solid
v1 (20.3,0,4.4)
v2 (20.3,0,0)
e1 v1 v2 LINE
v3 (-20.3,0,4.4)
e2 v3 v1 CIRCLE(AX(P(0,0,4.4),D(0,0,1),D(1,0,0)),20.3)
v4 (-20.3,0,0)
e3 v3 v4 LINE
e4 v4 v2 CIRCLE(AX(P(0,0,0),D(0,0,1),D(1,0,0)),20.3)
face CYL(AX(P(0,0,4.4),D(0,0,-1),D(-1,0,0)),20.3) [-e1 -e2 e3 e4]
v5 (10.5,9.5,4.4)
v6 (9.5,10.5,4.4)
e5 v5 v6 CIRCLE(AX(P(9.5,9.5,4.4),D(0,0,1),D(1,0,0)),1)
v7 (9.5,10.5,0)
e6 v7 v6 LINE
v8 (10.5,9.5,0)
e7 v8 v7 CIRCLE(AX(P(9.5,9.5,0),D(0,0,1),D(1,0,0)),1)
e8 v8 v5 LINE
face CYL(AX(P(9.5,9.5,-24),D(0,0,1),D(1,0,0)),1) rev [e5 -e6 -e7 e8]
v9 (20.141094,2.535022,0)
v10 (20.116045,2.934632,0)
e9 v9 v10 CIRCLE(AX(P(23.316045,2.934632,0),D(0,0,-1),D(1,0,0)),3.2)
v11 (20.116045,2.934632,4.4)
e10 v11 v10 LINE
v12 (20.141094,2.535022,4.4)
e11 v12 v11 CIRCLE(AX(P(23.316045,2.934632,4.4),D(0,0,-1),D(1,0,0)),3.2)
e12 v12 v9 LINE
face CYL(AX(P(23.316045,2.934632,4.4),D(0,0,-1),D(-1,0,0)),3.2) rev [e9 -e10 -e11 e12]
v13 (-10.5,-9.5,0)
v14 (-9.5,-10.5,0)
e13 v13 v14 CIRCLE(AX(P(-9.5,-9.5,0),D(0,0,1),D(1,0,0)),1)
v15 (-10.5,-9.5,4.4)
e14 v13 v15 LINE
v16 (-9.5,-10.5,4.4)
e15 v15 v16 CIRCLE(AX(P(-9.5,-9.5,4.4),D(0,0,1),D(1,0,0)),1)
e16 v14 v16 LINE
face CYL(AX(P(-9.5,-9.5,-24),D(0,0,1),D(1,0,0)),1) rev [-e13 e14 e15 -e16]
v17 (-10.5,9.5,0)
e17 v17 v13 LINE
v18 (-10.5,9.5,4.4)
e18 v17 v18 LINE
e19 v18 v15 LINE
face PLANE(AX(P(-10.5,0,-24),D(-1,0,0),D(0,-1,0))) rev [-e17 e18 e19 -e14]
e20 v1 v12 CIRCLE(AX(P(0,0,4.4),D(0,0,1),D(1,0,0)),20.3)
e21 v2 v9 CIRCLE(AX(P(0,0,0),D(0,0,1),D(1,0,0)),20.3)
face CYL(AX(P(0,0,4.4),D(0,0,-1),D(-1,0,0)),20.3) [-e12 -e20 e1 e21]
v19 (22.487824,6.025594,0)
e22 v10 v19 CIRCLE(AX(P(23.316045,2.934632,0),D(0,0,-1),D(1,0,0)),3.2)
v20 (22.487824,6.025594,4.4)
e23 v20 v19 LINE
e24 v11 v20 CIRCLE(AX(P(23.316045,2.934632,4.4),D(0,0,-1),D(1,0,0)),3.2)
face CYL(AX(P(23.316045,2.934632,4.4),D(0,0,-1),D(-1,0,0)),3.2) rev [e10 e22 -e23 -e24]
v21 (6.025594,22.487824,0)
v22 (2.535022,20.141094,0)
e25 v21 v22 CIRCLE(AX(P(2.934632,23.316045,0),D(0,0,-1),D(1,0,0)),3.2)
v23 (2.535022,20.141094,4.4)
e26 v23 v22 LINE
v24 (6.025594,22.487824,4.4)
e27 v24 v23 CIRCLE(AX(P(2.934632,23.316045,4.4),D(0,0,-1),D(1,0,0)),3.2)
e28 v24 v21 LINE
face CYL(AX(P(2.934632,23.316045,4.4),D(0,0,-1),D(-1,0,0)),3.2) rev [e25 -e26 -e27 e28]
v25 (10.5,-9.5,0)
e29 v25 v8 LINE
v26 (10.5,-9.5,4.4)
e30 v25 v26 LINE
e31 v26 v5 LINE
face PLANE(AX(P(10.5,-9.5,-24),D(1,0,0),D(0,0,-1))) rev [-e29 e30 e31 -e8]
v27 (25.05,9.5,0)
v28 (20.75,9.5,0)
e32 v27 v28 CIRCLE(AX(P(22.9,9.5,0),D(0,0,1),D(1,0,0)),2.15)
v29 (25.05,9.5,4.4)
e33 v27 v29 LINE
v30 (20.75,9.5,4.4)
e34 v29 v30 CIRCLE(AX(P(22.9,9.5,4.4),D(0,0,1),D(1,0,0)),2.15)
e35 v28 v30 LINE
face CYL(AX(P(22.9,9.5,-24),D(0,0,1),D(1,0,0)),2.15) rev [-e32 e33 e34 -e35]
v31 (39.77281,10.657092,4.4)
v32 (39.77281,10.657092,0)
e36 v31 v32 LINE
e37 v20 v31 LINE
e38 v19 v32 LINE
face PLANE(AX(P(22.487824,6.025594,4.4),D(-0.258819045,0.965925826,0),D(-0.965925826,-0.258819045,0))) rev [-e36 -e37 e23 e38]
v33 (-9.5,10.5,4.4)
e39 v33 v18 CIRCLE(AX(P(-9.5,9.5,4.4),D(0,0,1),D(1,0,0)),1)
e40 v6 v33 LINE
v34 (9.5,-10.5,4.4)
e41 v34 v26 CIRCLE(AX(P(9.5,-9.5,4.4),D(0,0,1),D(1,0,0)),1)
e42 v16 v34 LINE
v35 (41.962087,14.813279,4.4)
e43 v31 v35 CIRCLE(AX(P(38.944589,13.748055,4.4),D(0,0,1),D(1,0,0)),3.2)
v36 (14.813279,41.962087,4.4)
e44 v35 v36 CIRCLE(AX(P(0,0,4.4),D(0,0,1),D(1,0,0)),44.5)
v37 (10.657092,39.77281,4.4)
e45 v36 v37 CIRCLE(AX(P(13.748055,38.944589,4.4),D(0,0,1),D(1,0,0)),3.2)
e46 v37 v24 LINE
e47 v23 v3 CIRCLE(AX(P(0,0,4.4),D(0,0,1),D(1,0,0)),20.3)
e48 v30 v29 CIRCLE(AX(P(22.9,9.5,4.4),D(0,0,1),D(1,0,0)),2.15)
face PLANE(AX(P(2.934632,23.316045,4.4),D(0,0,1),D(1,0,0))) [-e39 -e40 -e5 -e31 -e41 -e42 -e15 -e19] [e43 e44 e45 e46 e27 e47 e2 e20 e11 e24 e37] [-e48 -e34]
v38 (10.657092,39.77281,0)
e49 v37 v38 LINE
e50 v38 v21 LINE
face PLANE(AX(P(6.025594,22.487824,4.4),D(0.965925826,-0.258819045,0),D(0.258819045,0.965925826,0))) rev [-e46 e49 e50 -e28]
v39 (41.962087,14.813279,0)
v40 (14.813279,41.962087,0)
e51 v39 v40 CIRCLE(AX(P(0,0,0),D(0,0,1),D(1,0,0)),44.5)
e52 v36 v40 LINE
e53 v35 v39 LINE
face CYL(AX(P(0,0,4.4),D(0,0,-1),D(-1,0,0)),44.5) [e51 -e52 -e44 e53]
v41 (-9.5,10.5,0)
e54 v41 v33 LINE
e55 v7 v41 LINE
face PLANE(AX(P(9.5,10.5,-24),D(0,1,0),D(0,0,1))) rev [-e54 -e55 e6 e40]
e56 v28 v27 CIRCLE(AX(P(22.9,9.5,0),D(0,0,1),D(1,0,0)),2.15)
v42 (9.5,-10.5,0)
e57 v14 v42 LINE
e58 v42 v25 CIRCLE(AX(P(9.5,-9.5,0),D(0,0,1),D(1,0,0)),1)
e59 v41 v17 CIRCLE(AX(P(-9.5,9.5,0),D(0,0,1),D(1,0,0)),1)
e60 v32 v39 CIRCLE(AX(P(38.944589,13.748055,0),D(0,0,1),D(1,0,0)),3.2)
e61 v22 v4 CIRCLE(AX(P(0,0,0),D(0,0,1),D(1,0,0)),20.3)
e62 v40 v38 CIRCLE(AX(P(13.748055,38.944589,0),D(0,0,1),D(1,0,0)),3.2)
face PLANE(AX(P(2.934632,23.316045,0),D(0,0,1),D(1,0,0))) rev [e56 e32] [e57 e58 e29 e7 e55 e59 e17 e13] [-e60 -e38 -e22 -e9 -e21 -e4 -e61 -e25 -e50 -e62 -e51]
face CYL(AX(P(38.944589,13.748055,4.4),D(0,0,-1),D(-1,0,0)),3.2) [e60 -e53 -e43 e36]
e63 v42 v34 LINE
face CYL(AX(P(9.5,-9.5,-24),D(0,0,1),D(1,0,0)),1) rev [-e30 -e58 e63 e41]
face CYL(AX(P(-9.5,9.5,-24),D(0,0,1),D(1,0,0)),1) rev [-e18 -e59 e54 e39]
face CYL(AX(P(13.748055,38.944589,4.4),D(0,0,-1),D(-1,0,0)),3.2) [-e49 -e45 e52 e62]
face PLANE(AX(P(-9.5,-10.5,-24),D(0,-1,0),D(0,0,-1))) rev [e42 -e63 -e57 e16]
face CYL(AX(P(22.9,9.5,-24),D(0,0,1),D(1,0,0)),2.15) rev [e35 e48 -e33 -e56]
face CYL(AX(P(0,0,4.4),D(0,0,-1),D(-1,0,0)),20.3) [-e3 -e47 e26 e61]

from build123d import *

# Parameters (mm, degrees)
LEVER_PLATE_4_4MM_DEPTH             = 4.4
SQUARE_DRIVE_AND_PIN_HOLE_SKETCH_R  = 2.15
SQUARE_DRIVE_AND_PIN_HOLE_CUT_DEPTH = 28.4


with BuildPart() as part:
    # Lever Plate Profile Sketch → Lever Plate 4.4mm (new body)
    with BuildSketch(Plane.XY):
        with BuildLine():
            Line((22.487823695, 6.025594199), (39.772809624, 10.65709222))
            ThreePointArc((39.772809624, 10.65709222), (41.775818518, 12.256700578), (41.962087077, 14.813279454))
            ThreePointArc((41.962087077, 14.813279454), (31.466251763, 31.466251763), (14.813279454, 41.962087077))
            ThreePointArc((14.813279454, 41.962087077), (12.256700578, 41.775818518), (10.65709222, 39.772809624))
            Line((10.65709222, 39.772809624), (6.025594199, 22.487823695))
            ThreePointArc((6.025594199, 22.487823695), (4.720025285, 20.660414916), (2.535022151, 20.14109388))
            ThreePointArc((2.535022151, 20.14109388), (-14.354267658, -14.354267658), (20.14109388, 2.535022151))
            ThreePointArc((20.14109388, 2.535022151), (20.660414916, 4.720025285), (22.487823695, 6.025594199))
        make_face()
    extrude(amount=LEVER_PLATE_4_4MM_DEPTH)

    # Square Drive and Pin Hole Sketch → Square Drive and Pin Hole Cut (cut)
    with BuildSketch(Plane.XY.offset(4.4)):
        with Locations((22.9, 9.5)):
            Circle(SQUARE_DRIVE_AND_PIN_HOLE_SKETCH_R)
        with BuildLine():
            Line((-10.5, 0), (-10.5, -9.5))
            ThreePointArc((-10.5, -9.5), (-10.207106781, -10.207106781), (-9.5, -10.5))
            Line((-9.5, -10.5), (9.5, -10.5))
            ThreePointArc((9.5, -10.5), (10.207106781, -10.207106781), (10.5, -9.5))
            Line((10.5, -9.5), (10.5, 9.5))
            ThreePointArc((10.5, 9.5), (10.207106781, 10.207106781), (9.5, 10.5))
            Line((9.5, 10.5), (-9.5, 10.5))
            ThreePointArc((-9.5, 10.5), (-10.207106781, 10.207106781), (-10.5, 9.5))
            Line((-10.5, 9.5), (-10.5, 0))
        make_face()
    extrude(amount=-SQUARE_DRIVE_AND_PIN_HOLE_CUT_DEPTH, mode=Mode.SUBTRACT)


solid = part.part
